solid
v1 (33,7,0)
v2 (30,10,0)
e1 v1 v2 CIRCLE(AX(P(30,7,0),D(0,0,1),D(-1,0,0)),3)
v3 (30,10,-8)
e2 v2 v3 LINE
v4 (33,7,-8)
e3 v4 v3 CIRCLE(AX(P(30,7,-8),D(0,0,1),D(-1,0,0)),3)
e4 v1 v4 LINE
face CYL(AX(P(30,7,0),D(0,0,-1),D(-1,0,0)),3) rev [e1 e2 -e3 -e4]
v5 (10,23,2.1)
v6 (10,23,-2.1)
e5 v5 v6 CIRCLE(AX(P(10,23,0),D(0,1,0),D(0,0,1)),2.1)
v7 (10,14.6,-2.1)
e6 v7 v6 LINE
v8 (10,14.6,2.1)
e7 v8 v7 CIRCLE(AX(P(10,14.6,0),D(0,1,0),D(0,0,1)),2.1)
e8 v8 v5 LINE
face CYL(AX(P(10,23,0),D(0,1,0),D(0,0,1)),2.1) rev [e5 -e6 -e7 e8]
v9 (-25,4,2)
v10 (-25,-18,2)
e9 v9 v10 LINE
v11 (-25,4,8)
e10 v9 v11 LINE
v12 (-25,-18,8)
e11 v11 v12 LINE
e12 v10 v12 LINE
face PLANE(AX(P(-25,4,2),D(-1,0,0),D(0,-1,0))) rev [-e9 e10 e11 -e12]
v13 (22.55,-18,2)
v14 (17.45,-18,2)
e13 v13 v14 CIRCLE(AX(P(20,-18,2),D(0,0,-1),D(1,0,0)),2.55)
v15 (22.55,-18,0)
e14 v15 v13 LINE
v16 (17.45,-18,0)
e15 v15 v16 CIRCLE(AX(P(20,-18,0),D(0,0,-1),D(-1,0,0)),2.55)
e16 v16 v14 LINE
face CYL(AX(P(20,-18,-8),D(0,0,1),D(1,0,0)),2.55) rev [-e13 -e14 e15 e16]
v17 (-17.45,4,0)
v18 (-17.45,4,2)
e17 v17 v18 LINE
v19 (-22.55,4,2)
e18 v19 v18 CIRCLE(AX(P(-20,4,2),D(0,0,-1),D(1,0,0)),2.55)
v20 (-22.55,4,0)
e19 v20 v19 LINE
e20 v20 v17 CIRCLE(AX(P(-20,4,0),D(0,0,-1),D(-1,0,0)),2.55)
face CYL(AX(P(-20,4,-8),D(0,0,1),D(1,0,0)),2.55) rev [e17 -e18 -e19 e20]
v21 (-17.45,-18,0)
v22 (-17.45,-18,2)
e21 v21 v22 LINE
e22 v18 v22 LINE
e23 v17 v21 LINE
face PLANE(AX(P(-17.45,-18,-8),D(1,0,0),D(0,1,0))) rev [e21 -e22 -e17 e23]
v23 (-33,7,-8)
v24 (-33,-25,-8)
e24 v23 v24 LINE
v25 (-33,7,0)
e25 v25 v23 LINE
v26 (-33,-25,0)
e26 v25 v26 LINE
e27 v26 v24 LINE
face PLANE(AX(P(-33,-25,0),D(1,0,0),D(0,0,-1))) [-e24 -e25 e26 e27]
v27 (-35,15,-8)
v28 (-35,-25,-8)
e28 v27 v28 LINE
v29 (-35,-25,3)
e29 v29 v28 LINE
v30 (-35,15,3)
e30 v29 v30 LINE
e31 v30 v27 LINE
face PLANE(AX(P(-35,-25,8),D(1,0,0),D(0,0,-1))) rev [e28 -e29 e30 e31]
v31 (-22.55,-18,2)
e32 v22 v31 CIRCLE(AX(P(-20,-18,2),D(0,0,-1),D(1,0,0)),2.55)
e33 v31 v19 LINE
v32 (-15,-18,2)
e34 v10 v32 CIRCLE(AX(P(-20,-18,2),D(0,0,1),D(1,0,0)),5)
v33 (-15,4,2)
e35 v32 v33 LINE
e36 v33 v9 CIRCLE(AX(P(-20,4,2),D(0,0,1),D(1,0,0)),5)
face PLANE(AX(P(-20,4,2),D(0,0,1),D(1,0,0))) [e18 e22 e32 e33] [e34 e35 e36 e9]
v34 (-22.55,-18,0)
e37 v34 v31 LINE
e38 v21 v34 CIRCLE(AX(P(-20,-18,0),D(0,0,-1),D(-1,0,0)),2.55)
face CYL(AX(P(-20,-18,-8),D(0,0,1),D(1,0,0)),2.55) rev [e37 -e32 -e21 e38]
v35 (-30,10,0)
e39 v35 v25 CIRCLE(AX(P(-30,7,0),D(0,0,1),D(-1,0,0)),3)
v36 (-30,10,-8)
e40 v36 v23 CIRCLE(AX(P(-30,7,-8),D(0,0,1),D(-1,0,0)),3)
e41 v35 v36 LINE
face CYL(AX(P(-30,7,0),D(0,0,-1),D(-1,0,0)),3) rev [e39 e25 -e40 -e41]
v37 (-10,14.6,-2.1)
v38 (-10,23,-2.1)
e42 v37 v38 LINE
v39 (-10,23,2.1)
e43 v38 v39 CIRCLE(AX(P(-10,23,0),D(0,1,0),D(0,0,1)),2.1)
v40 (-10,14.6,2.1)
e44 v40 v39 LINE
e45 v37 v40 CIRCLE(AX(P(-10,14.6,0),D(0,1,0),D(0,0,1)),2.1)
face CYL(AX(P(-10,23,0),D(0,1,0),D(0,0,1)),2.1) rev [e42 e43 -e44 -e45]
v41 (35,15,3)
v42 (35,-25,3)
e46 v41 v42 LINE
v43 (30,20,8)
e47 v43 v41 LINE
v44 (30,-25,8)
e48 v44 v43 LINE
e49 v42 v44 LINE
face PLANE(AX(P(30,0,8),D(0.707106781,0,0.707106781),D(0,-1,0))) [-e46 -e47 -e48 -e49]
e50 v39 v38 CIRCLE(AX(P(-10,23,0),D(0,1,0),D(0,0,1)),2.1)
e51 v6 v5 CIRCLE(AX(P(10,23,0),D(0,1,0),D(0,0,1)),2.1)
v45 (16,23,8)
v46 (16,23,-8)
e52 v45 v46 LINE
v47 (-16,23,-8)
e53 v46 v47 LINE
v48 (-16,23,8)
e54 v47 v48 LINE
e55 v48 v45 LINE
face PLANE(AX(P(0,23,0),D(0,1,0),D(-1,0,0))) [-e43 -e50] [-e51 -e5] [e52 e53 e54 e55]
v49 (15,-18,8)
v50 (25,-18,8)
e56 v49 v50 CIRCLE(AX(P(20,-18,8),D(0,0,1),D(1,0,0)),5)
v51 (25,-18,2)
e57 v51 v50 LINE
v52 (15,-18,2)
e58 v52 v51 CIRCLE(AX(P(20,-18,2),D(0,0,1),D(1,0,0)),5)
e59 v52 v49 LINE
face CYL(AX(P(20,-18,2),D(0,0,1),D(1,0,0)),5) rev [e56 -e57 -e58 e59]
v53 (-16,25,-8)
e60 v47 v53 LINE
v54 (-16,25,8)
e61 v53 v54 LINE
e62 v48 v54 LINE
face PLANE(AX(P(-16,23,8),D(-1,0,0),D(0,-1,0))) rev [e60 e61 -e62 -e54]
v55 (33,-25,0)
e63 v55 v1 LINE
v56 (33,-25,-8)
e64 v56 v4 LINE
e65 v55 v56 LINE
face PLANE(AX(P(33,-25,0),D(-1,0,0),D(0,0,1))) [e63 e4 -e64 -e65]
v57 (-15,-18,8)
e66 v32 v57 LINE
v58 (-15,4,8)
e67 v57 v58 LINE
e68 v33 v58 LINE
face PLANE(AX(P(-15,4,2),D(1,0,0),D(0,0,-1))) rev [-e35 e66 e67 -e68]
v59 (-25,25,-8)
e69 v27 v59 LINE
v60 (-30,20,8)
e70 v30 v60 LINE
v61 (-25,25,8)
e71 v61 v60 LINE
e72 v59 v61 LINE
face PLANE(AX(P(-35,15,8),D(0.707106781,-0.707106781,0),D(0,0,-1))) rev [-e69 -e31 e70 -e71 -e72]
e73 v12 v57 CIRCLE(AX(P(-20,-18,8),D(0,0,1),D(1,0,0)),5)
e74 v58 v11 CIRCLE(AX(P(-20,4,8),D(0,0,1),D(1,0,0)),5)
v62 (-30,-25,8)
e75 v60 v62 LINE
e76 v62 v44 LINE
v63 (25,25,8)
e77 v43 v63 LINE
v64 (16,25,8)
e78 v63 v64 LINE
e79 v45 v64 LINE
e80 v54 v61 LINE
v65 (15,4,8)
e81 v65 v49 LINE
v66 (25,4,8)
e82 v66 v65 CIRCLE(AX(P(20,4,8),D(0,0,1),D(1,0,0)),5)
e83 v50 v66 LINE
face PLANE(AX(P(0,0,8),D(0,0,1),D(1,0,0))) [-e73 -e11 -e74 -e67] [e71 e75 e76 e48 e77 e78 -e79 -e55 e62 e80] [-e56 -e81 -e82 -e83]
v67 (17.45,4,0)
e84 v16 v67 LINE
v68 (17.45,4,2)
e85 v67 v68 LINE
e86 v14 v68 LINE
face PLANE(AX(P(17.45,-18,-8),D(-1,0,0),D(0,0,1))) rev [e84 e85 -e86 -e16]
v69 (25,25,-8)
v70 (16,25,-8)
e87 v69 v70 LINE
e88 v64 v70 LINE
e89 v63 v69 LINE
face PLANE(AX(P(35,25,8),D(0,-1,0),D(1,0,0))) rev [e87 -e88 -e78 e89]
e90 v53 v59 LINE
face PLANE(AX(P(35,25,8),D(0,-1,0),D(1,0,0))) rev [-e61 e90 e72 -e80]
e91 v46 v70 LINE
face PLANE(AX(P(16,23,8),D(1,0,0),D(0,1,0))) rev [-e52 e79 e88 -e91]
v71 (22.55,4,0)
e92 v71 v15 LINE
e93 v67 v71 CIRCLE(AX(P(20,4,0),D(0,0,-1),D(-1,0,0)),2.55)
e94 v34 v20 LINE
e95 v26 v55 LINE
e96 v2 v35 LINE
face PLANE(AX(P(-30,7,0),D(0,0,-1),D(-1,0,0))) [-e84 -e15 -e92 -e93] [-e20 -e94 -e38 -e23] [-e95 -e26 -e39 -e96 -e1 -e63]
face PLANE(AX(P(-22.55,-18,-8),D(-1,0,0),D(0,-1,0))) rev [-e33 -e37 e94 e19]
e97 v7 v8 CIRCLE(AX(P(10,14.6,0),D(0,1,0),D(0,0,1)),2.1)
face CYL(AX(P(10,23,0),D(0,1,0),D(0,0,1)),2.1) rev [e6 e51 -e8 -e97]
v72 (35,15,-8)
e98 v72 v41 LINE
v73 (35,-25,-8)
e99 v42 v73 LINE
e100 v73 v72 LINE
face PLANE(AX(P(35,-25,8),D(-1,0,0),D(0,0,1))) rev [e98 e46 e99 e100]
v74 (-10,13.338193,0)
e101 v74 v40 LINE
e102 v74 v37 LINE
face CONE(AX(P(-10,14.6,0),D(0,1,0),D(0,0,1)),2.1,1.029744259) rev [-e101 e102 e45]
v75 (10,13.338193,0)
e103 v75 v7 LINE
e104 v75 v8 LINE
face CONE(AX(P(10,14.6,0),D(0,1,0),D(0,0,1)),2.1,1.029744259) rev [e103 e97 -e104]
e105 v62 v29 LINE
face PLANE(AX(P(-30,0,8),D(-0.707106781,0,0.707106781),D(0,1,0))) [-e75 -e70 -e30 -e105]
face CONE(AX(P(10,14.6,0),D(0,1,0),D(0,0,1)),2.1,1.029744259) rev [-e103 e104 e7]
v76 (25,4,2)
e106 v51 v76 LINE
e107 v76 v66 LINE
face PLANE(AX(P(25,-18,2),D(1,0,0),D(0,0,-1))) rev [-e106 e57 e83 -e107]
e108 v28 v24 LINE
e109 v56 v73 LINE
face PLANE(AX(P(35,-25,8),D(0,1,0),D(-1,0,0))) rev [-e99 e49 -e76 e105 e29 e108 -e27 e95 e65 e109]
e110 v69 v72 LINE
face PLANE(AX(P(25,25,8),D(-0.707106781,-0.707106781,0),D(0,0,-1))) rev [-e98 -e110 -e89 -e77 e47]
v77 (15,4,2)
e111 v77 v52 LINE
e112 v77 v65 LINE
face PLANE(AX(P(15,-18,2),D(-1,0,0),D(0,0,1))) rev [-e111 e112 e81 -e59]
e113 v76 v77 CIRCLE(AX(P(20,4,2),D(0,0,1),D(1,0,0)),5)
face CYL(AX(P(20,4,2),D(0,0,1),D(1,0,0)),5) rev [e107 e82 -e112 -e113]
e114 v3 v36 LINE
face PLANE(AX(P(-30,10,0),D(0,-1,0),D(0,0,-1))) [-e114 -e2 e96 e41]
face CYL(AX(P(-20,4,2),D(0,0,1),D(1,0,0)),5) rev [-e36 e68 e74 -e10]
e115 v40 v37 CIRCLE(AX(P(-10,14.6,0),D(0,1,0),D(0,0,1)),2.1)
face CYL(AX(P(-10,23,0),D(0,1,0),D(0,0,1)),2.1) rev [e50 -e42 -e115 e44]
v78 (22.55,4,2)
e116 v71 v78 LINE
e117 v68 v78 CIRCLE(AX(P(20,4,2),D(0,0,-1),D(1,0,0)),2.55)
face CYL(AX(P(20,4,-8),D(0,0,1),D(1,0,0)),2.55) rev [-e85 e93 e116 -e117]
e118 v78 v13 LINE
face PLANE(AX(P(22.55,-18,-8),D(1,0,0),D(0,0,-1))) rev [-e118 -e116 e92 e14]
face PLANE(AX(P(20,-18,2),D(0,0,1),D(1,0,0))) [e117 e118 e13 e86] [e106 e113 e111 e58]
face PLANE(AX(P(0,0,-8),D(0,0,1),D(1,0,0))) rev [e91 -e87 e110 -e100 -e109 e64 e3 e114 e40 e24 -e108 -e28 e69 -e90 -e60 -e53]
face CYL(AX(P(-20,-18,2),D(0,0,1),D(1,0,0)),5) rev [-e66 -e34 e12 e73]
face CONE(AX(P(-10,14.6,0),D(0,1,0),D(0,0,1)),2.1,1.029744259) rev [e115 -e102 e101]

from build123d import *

# Parameters (mm, degrees)
SKETCH1_W             = 70
SKETCH1_H             = 50
EXTRUDE1_DEPTH        = 8
SKETCH2_W             = 32
SKETCH2_H             = 16
EXTRUDE2_DEPTH        = 2
M5_TAPPED_HOLE1_D     = 4.2
M5_TAPPED_HOLE1_DEPTH = 8.4
M5_TAPPED_HOLE1_TIP   = 1.2618073
EXTRUDE3_DEPTH        = 8
EXTRUDE4_DEPTH        = 46.891175622
EXTRUDE5_DEPTH        = 6
CHAMFER1_SIZE         = 10
CHAMFER2_SIZE         = 5


with BuildPart() as part:
    # Sketch1 → Extrude1 (new, symmetric)
    with BuildSketch(Plane.XY):
        Rectangle(SKETCH1_W, SKETCH1_H)
    extrude(amount=EXTRUDE1_DEPTH, both=True)

    # Sketch2 → Extrude2 (cut)
    with BuildSketch(Plane(origin=(0, 25, 0), x_dir=(1, 0, 0), z_dir=(0, 1, 0))):
        Rectangle(SKETCH2_W, SKETCH2_H)
    extrude(amount=-EXTRUDE2_DEPTH, mode=Mode.SUBTRACT)

    # M5 Tapped Hole1
    with Locations(Plane(origin=(0, 23, 0), x_dir=(1, 0, 0), z_dir=(0, 1, 0))):
        with Locations((-10, 0), (10, 0)):
            Hole(M5_TAPPED_HOLE1_D / 2, depth=M5_TAPPED_HOLE1_DEPTH)
            with Locations((0, 0, -(M5_TAPPED_HOLE1_DEPTH + M5_TAPPED_HOLE1_TIP / 2))):  # 118° drill point
                Cone(0, M5_TAPPED_HOLE1_D / 2, M5_TAPPED_HOLE1_TIP, mode=Mode.SUBTRACT)

    # Sketch5 → Extrude3 (cut)
    with BuildSketch(Plane.XY.offset(-8)):
        with BuildLine():
            Line((-33, -25), (33, -25))
            Line((33, -25), (33, 7))
            ThreePointArc((33, 7), (32.121320344, 9.121320344), (30, 10))
            Line((30, 10), (-30, 10))
            ThreePointArc((-30, 10), (-32.121320344, 9.121320344), (-33, 7))
            Line((-33, 7), (-33, -25))
        make_face()
    extrude(amount=EXTRUDE3_DEPTH, mode=Mode.SUBTRACT)

    # Sketch6 → Extrude4 (cut, through all)
    with BuildSketch(Plane.XY.offset(8)):
        with BuildLine():
            Line((-22.55, -18), (-22.55, 4))
            ThreePointArc((-22.55, 4), (-20, 6.55), (-17.45, 4))
            Line((-17.45, 4), (-17.45, -18))
            ThreePointArc((-17.45, -18), (-20, -20.55), (-22.55, -18))
        make_face()
        with BuildLine():
            Line((17.45, -18), (17.45, 4))
            ThreePointArc((17.45, 4), (20, 6.55), (22.55, 4))
            Line((22.55, 4), (22.55, -18))
            ThreePointArc((22.55, -18), (20, -20.55), (17.45, -18))
        make_face()
    extrude(amount=-EXTRUDE4_DEPTH, mode=Mode.SUBTRACT)

    # Sketch7 → Extrude5 (cut)
    with BuildSketch(Plane.XY.offset(8)):
        with BuildLine():
            Line((15, -18), (15, 4))
            ThreePointArc((15, 4), (20, 9), (25, 4))
            Line((25, 4), (25, -18))
            ThreePointArc((25, -18), (20, -23), (15, -18))
        make_face()
        with BuildLine():
            Line((-15, 4), (-15, -18))
            ThreePointArc((-15, -18), (-20, -23), (-25, -18))
            Line((-25, -18), (-25, 4))
            ThreePointArc((-25, 4), (-20, 9), (-15, 4))
        make_face()
    extrude(amount=-EXTRUDE5_DEPTH, mode=Mode.SUBTRACT)

    # Chamfer1
    chamfer1_edges = [part.edges().sort_by_distance(p)[0] for p in [
        (-35, 25, 0),
        (35, 25, 0),
    ]]
    chamfer(chamfer1_edges, length=CHAMFER1_SIZE)

    # Chamfer2
    chamfer2_edges = [part.edges().sort_by_distance(p)[0] for p in [
        (35, -5, 8),
        (-35, -5, 8),
    ]]
    chamfer(chamfer2_edges, length=CHAMFER2_SIZE)


solid = part.part
